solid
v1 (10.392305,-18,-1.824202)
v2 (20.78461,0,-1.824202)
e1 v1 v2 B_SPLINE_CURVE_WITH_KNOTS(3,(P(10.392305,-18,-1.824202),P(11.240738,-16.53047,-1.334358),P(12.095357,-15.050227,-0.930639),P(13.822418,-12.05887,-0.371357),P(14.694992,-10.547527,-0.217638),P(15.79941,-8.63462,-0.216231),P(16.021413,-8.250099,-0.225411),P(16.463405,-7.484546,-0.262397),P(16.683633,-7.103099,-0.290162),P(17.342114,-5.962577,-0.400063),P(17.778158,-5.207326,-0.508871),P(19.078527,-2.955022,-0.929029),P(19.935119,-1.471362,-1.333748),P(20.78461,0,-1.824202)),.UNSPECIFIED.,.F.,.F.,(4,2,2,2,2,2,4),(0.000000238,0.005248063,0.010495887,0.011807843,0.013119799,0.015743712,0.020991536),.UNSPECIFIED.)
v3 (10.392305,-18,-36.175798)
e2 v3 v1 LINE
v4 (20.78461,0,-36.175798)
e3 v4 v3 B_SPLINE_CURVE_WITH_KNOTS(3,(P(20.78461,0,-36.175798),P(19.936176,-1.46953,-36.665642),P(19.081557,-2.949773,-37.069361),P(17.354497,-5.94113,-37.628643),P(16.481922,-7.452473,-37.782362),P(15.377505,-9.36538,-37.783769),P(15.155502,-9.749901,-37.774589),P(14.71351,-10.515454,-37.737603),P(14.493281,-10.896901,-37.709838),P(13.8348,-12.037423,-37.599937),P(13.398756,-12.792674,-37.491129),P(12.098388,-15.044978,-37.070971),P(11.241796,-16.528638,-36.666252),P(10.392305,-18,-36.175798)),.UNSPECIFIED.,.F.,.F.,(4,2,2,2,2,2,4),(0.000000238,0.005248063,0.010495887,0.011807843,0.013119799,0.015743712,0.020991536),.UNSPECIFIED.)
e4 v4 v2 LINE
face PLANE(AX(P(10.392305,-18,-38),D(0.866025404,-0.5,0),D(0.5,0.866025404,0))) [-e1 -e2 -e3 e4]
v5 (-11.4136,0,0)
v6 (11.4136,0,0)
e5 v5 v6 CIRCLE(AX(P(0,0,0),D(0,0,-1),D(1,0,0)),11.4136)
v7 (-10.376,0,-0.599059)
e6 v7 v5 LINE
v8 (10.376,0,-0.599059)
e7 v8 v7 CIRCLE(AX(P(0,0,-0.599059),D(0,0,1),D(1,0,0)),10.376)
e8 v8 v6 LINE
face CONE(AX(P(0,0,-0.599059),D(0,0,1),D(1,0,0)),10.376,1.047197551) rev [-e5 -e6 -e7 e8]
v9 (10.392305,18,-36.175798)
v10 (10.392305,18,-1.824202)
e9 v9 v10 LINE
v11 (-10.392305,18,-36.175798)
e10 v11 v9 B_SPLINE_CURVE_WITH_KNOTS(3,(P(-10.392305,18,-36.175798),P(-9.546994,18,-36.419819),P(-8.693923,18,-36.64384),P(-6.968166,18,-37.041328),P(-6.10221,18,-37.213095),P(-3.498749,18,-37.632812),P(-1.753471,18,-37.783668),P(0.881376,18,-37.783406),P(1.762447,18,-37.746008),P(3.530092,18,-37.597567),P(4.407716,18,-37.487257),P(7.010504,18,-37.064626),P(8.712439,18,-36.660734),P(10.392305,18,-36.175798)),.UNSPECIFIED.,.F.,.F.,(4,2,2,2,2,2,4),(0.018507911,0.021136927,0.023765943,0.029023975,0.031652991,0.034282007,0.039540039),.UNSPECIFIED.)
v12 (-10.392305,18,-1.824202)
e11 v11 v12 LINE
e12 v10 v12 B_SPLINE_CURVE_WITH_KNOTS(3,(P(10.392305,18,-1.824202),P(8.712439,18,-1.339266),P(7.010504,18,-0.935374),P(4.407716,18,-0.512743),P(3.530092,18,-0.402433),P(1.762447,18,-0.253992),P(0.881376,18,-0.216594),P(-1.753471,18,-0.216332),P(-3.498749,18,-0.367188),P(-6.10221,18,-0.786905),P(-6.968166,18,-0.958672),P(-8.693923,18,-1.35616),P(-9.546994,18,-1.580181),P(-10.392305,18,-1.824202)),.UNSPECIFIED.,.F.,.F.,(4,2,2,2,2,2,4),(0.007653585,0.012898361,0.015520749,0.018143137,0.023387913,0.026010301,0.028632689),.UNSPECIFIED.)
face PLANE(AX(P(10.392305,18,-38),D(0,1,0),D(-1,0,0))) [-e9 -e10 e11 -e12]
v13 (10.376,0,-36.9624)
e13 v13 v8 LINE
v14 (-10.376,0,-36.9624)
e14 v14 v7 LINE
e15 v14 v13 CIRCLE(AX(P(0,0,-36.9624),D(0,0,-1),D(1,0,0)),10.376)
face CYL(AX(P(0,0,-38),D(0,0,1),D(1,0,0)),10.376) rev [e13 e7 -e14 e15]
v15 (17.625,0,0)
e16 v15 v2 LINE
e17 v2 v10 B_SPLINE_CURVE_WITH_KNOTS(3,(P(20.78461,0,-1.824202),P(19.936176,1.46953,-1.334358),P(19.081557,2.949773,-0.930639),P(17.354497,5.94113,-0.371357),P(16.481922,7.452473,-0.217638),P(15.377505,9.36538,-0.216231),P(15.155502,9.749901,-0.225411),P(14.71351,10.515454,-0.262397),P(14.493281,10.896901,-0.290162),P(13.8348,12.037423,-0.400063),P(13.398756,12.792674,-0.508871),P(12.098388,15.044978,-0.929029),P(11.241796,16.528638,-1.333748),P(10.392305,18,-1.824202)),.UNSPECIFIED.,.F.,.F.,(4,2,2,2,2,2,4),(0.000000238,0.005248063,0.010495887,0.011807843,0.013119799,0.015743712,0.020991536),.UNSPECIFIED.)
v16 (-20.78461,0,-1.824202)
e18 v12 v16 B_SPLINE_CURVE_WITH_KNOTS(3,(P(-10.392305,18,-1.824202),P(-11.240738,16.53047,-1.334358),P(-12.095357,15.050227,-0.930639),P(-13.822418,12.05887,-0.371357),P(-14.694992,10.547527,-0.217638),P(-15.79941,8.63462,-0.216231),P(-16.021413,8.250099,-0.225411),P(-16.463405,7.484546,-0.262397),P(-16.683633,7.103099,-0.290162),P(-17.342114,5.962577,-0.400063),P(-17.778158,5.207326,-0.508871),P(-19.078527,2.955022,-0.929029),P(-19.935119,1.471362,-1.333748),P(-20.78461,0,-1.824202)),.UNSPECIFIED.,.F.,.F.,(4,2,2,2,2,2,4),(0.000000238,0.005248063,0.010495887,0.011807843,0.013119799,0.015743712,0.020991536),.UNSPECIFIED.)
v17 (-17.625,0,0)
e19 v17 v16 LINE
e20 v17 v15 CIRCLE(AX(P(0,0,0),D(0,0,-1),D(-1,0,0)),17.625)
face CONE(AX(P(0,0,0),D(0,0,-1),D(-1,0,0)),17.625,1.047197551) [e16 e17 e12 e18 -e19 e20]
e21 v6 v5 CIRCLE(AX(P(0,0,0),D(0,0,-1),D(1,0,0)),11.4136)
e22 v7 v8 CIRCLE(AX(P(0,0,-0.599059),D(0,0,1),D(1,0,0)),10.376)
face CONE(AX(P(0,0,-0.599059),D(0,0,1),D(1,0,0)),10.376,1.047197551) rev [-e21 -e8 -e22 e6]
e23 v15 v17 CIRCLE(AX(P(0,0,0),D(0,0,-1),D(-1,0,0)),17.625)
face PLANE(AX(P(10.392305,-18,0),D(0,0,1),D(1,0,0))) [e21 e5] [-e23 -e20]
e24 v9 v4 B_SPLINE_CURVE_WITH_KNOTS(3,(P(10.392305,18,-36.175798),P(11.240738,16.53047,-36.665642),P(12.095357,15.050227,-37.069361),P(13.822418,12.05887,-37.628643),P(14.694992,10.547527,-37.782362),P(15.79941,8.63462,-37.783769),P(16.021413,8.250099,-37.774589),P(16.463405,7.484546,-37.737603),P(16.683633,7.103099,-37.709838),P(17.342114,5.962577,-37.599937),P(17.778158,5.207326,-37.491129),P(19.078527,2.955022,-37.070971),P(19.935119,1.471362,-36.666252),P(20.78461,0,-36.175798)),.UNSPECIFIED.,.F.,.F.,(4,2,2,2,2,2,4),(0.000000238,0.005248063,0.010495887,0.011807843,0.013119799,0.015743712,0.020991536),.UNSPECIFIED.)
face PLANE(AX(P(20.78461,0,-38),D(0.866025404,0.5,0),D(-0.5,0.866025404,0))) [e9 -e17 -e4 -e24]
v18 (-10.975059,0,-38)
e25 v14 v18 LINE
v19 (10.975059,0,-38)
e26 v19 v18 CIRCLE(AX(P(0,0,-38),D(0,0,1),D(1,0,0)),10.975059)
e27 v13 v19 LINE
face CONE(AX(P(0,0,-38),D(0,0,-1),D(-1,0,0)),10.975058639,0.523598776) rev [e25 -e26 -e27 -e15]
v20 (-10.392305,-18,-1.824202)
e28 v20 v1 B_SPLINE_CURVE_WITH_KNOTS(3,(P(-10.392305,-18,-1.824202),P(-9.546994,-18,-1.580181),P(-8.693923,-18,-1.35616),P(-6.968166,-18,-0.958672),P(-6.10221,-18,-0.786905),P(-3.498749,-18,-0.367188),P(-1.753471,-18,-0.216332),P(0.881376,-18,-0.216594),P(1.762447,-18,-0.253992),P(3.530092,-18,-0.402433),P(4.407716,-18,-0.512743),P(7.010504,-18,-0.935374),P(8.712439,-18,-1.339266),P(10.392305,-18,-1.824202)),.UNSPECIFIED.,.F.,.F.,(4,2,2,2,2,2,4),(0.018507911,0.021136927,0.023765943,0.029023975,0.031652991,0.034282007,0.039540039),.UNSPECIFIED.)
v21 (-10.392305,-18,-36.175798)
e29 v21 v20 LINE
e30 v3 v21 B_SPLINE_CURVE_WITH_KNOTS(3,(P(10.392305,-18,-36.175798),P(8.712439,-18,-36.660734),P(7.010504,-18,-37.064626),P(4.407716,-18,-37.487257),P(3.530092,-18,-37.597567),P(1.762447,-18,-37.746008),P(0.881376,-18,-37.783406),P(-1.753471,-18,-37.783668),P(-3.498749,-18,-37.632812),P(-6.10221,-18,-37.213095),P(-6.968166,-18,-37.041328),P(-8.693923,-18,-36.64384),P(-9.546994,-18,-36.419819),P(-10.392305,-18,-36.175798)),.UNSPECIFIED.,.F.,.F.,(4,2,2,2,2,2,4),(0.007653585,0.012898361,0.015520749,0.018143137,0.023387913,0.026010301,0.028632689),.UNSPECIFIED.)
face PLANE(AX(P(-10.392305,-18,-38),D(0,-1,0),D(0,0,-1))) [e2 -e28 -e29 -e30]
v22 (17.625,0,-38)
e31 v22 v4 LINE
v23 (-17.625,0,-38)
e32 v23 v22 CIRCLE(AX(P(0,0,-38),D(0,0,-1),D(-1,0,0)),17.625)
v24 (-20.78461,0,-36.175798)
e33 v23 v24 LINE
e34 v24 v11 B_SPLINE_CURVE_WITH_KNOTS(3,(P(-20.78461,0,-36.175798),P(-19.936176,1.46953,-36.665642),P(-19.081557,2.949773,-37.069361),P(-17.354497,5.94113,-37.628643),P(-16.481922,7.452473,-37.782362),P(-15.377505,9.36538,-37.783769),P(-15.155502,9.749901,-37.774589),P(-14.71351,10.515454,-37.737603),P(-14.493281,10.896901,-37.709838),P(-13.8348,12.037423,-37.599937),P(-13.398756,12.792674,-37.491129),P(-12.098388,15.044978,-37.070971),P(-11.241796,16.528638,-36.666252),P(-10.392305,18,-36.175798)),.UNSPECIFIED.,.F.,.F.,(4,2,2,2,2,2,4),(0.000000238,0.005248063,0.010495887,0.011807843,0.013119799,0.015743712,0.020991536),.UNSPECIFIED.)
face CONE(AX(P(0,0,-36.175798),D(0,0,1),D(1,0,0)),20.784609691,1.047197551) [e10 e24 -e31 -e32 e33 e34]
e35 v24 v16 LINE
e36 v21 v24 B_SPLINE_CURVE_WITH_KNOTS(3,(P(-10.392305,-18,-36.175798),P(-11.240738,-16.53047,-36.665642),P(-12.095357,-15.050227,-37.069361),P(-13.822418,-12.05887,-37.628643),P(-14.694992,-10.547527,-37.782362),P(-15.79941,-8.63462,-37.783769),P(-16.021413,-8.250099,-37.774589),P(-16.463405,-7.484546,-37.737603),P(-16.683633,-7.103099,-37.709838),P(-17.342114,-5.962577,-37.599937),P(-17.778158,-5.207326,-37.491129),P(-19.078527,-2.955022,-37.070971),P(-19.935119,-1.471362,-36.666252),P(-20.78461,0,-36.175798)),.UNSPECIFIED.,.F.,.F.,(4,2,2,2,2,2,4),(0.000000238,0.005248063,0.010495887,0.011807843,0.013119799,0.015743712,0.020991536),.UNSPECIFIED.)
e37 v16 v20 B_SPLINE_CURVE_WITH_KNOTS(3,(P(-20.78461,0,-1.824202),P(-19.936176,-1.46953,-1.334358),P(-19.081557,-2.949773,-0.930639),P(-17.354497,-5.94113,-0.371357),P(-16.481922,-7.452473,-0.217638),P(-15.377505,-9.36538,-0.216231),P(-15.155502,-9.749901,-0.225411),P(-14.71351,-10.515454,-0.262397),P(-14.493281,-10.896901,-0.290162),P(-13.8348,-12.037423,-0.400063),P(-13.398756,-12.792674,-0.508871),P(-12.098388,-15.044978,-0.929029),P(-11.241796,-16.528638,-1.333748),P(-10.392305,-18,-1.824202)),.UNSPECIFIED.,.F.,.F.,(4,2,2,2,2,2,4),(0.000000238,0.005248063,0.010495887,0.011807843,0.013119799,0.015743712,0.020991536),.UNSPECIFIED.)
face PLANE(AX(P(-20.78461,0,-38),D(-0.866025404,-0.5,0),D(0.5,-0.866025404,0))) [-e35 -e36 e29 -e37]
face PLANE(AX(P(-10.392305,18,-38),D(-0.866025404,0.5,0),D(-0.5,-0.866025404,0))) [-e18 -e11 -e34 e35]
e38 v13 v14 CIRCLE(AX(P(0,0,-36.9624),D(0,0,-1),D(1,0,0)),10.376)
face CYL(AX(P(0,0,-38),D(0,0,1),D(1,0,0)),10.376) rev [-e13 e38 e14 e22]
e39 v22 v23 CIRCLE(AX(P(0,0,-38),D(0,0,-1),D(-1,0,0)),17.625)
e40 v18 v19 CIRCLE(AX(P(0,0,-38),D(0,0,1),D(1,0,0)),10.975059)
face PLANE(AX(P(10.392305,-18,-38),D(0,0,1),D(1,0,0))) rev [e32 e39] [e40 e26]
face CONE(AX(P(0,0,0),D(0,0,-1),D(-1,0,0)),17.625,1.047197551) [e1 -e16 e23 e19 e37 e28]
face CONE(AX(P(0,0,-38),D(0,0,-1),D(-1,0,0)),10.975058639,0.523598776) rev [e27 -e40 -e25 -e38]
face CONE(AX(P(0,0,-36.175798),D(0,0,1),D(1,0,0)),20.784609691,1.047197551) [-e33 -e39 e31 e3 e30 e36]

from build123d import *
from OCP.BRepFilletAPI import BRepFilletAPI_MakeChamfer

# Parameters (mm, degrees)
SKETCH1_R        = 10.376
BASENUT_DEPTH    = 38
ENDCHAMFER_SIZE  = 1.0376
ENDCHAMFER_SIZE2 = 0.599058639


with BuildPart() as part:
    # Sketch1 → BaseNut (new body)
    with BuildSketch(Plane.XY):
        Polygon((10.392304845, -18), (20.784609691, 0), (10.392304845, 18), (-10.392304845, 18), (-20.784609691, 0), (-10.392304845, -18), align=None)
        Circle(SKETCH1_R, mode=Mode.SUBTRACT)
    extrude(amount=-BASENUT_DEPTH)

    # Sketch2 → Double-Chamfer (revolve, cut)
    with BuildSketch(Plane(origin=(0, 0, 0), x_dir=(1, 0, 0), z_dir=(0, 1, 0))):
        Polygon((-20.784609691, 38), (-17.625, 38), (-20.784609691, 36.175798494), align=None)
        Polygon((-20.784609691, 1.824201506), (-20.784609691, 0), (-17.625, 0), align=None)
    revolve(axis=Axis((0, 0, -3.375940562), (0, 0, 1)), mode=Mode.SUBTRACT)

    # EndChamfer: one chamfer whose edges measure the first distance from different faces: ONE call of the kernel's chamfer builder (chamfer() names one face for all edges)
    endchamfer_edges_1 = [part.edges().sort_by_distance(p)[0] for p in [
        (-10.376, 0, -38),
    ]]
    endchamfer_side_1 = [part.faces().sort_by_distance(p)[0] for p in [
        (-10.376, 0, -19),
    ]]
    endchamfer_edges_2 = [part.edges().sort_by_distance(p)[0] for p in [
        (-10.376, 0, 0),
    ]]
    endchamfer_side_2 = [part.faces().sort_by_distance(p)[0] for p in [
        (17.126489719, 0, 0),
    ]]
    endchamfer = BRepFilletAPI_MakeChamfer(part.part.solid().wrapped)
    for e in endchamfer_edges_1:
        endchamfer.Add(ENDCHAMFER_SIZE, ENDCHAMFER_SIZE2, e.wrapped, endchamfer_side_1[0].wrapped)  # the first distance lies on this face
    for e in endchamfer_edges_2:
        endchamfer.Add(ENDCHAMFER_SIZE, ENDCHAMFER_SIZE2, e.wrapped, endchamfer_side_2[0].wrapped)  # the first distance lies on this face
    add(Compound.cast(endchamfer.Shape()), mode=Mode.REPLACE)


solid = part.part
